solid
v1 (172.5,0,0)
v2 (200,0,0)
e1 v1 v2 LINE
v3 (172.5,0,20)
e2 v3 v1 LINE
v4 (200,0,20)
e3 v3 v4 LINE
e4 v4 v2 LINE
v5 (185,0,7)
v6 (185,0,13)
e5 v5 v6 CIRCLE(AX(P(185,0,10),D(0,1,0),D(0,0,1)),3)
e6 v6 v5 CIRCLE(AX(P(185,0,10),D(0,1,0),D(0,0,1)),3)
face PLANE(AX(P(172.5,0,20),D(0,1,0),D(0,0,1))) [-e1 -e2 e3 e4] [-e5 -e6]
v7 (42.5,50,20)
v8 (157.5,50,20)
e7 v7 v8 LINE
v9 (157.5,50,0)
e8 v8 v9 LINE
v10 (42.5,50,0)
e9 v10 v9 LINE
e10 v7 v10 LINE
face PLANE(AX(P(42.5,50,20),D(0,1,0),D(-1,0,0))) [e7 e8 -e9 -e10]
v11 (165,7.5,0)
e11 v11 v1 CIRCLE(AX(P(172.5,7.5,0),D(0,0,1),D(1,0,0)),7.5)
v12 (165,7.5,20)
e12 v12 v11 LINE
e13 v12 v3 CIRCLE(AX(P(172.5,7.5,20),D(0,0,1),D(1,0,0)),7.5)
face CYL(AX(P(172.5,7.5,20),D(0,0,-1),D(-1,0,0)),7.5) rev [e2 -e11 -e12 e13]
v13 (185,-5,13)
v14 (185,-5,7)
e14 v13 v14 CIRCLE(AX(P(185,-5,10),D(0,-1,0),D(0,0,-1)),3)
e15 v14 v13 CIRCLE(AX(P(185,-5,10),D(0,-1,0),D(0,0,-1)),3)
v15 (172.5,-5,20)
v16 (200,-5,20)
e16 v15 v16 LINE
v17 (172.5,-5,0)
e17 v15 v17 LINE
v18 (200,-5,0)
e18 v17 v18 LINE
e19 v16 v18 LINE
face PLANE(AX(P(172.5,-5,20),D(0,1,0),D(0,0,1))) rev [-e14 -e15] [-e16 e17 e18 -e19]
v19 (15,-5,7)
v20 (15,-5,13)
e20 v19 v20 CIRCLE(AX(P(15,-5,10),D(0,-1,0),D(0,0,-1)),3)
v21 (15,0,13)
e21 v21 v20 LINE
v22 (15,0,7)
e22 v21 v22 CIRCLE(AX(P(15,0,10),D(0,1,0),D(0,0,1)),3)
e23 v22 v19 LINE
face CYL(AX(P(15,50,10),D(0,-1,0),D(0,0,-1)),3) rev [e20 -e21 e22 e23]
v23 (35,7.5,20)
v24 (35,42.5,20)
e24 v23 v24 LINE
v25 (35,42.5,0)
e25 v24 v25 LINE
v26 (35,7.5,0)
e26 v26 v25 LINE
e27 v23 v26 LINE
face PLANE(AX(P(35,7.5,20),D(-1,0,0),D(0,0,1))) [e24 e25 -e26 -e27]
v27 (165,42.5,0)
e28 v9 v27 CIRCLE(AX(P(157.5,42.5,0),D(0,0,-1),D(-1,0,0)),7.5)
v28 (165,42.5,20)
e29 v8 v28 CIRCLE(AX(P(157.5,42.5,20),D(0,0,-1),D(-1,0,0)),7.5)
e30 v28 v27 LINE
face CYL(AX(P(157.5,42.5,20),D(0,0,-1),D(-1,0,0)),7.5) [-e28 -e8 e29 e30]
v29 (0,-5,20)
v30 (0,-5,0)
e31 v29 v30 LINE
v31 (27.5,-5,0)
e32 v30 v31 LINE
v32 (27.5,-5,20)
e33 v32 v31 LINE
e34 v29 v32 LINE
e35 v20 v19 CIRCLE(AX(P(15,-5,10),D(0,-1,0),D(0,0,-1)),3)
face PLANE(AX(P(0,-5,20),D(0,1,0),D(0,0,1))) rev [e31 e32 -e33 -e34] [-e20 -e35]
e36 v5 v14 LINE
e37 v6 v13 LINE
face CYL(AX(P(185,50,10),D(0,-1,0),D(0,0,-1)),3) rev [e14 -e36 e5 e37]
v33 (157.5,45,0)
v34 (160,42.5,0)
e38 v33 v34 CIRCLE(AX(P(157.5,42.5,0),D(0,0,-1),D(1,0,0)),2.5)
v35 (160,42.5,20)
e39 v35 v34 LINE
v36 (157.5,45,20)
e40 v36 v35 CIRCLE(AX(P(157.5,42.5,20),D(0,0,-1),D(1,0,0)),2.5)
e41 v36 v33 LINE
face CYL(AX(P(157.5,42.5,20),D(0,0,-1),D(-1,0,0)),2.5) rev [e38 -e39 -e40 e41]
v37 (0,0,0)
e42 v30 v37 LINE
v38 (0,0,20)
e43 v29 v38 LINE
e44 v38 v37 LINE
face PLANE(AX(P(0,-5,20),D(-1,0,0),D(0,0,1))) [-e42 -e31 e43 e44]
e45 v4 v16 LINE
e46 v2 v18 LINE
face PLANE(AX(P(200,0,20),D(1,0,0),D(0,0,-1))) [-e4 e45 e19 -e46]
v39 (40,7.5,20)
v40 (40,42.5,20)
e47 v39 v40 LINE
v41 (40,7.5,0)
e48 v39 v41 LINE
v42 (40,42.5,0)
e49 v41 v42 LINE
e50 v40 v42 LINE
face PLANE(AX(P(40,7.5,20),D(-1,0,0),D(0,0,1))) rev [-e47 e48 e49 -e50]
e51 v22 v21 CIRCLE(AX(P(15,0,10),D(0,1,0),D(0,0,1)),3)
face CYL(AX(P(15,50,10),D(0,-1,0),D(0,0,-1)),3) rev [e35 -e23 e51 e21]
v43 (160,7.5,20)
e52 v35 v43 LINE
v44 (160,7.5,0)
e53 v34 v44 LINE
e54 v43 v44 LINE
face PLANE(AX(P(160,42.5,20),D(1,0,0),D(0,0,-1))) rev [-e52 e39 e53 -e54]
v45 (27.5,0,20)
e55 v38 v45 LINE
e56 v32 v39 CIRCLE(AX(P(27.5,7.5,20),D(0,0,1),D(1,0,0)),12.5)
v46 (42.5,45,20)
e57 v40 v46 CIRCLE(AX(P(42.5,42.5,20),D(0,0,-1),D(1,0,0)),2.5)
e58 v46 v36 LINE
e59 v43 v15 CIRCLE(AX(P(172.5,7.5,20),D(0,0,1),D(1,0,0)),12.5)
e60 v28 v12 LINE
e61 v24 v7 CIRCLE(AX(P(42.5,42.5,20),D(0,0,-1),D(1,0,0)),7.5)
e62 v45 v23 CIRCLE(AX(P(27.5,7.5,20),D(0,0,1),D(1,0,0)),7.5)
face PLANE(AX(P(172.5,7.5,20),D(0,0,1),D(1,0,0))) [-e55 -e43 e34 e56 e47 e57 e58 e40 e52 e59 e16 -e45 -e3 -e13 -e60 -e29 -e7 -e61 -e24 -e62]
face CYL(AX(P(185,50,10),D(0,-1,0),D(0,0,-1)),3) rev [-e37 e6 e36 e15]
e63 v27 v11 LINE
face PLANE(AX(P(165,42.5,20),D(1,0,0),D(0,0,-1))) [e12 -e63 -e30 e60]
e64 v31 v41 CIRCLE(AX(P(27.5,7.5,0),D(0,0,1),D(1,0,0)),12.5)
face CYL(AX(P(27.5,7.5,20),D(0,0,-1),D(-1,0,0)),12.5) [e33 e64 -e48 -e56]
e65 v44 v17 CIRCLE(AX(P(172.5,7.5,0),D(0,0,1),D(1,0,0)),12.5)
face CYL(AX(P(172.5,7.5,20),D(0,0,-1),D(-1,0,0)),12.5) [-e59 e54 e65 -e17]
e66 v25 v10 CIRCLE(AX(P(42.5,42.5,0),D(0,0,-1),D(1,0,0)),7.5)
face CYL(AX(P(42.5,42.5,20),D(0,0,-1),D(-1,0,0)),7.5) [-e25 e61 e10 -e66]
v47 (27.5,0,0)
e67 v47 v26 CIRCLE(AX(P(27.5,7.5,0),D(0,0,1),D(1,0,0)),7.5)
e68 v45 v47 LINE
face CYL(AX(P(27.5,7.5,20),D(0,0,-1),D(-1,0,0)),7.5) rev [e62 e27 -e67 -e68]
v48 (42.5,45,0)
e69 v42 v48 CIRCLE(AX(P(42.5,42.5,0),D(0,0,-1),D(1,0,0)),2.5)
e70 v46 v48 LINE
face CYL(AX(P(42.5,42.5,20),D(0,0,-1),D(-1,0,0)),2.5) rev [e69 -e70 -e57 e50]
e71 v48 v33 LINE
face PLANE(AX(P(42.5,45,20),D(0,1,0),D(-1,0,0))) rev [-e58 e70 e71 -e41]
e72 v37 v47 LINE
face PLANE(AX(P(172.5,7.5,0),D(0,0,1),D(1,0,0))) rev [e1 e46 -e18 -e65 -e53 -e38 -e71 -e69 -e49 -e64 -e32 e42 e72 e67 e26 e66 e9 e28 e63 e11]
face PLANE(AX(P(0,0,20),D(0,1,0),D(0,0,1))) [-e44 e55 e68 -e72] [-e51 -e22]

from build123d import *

# Parameters (mm, degrees)
EXTRUDE_1_DEPTH     = 20
SKETCH_2_R          = 3
CUT_EXTRUDE_1_DEPTH = 209.386659842


with BuildPart() as part:
    # 草图1 → 拉伸-薄壁1 (new body)
    with BuildSketch(Plane.XY):
        with BuildLine():
            Line((0, 0), (27.5, 0))
            ThreePointArc((27.5, 0), (32.803300859, 2.196699141), (35, 7.5))
            Line((35, 7.5), (35, 42.5))
            ThreePointArc((35, 42.5), (37.196699141, 47.803300859), (42.5, 50))
            Line((42.5, 50), (157.5, 50))
            ThreePointArc((157.5, 50), (162.803300859, 47.803300859), (165, 42.5))
            Line((165, 42.5), (165, 7.5))
            ThreePointArc((165, 7.5), (167.196699141, 2.196699141), (172.5, 0))
            Line((172.5, 0), (200, 0))
            Line((200, 0), (200, -5))
            Line((200, -5), (172.5, -5))
            ThreePointArc((172.5, -5), (163.661165235, -1.338834765), (160, 7.5))
            Line((160, 7.5), (160, 42.5))
            ThreePointArc((160, 42.5), (159.267766953, 44.267766953), (157.5, 45))
            Line((157.5, 45), (42.5, 45))
            ThreePointArc((42.5, 45), (40.732233047, 44.267766953), (40, 42.5))
            Line((40, 42.5), (40, 7.5))
            ThreePointArc((40, 7.5), (36.338834765, -1.338834765), (27.5, -5))
            Line((27.5, -5), (0, -5))
            Line((0, -5), (0, 0))
        make_face()
    extrude(amount=EXTRUDE_1_DEPTH)

    # 草图2 → 切除-拉伸1 (cut, through all)
    with BuildSketch(Plane.XZ.offset(5)):
        with Locations(Location((15, 10, 0), (0, 0, 270))):
            Circle(SKETCH_2_R)
        with Locations(Location((185, 10, 0), (0, 0, 270))):
            Circle(SKETCH_2_R)
    extrude(amount=-CUT_EXTRUDE_1_DEPTH, mode=Mode.SUBTRACT)


solid = part.part
